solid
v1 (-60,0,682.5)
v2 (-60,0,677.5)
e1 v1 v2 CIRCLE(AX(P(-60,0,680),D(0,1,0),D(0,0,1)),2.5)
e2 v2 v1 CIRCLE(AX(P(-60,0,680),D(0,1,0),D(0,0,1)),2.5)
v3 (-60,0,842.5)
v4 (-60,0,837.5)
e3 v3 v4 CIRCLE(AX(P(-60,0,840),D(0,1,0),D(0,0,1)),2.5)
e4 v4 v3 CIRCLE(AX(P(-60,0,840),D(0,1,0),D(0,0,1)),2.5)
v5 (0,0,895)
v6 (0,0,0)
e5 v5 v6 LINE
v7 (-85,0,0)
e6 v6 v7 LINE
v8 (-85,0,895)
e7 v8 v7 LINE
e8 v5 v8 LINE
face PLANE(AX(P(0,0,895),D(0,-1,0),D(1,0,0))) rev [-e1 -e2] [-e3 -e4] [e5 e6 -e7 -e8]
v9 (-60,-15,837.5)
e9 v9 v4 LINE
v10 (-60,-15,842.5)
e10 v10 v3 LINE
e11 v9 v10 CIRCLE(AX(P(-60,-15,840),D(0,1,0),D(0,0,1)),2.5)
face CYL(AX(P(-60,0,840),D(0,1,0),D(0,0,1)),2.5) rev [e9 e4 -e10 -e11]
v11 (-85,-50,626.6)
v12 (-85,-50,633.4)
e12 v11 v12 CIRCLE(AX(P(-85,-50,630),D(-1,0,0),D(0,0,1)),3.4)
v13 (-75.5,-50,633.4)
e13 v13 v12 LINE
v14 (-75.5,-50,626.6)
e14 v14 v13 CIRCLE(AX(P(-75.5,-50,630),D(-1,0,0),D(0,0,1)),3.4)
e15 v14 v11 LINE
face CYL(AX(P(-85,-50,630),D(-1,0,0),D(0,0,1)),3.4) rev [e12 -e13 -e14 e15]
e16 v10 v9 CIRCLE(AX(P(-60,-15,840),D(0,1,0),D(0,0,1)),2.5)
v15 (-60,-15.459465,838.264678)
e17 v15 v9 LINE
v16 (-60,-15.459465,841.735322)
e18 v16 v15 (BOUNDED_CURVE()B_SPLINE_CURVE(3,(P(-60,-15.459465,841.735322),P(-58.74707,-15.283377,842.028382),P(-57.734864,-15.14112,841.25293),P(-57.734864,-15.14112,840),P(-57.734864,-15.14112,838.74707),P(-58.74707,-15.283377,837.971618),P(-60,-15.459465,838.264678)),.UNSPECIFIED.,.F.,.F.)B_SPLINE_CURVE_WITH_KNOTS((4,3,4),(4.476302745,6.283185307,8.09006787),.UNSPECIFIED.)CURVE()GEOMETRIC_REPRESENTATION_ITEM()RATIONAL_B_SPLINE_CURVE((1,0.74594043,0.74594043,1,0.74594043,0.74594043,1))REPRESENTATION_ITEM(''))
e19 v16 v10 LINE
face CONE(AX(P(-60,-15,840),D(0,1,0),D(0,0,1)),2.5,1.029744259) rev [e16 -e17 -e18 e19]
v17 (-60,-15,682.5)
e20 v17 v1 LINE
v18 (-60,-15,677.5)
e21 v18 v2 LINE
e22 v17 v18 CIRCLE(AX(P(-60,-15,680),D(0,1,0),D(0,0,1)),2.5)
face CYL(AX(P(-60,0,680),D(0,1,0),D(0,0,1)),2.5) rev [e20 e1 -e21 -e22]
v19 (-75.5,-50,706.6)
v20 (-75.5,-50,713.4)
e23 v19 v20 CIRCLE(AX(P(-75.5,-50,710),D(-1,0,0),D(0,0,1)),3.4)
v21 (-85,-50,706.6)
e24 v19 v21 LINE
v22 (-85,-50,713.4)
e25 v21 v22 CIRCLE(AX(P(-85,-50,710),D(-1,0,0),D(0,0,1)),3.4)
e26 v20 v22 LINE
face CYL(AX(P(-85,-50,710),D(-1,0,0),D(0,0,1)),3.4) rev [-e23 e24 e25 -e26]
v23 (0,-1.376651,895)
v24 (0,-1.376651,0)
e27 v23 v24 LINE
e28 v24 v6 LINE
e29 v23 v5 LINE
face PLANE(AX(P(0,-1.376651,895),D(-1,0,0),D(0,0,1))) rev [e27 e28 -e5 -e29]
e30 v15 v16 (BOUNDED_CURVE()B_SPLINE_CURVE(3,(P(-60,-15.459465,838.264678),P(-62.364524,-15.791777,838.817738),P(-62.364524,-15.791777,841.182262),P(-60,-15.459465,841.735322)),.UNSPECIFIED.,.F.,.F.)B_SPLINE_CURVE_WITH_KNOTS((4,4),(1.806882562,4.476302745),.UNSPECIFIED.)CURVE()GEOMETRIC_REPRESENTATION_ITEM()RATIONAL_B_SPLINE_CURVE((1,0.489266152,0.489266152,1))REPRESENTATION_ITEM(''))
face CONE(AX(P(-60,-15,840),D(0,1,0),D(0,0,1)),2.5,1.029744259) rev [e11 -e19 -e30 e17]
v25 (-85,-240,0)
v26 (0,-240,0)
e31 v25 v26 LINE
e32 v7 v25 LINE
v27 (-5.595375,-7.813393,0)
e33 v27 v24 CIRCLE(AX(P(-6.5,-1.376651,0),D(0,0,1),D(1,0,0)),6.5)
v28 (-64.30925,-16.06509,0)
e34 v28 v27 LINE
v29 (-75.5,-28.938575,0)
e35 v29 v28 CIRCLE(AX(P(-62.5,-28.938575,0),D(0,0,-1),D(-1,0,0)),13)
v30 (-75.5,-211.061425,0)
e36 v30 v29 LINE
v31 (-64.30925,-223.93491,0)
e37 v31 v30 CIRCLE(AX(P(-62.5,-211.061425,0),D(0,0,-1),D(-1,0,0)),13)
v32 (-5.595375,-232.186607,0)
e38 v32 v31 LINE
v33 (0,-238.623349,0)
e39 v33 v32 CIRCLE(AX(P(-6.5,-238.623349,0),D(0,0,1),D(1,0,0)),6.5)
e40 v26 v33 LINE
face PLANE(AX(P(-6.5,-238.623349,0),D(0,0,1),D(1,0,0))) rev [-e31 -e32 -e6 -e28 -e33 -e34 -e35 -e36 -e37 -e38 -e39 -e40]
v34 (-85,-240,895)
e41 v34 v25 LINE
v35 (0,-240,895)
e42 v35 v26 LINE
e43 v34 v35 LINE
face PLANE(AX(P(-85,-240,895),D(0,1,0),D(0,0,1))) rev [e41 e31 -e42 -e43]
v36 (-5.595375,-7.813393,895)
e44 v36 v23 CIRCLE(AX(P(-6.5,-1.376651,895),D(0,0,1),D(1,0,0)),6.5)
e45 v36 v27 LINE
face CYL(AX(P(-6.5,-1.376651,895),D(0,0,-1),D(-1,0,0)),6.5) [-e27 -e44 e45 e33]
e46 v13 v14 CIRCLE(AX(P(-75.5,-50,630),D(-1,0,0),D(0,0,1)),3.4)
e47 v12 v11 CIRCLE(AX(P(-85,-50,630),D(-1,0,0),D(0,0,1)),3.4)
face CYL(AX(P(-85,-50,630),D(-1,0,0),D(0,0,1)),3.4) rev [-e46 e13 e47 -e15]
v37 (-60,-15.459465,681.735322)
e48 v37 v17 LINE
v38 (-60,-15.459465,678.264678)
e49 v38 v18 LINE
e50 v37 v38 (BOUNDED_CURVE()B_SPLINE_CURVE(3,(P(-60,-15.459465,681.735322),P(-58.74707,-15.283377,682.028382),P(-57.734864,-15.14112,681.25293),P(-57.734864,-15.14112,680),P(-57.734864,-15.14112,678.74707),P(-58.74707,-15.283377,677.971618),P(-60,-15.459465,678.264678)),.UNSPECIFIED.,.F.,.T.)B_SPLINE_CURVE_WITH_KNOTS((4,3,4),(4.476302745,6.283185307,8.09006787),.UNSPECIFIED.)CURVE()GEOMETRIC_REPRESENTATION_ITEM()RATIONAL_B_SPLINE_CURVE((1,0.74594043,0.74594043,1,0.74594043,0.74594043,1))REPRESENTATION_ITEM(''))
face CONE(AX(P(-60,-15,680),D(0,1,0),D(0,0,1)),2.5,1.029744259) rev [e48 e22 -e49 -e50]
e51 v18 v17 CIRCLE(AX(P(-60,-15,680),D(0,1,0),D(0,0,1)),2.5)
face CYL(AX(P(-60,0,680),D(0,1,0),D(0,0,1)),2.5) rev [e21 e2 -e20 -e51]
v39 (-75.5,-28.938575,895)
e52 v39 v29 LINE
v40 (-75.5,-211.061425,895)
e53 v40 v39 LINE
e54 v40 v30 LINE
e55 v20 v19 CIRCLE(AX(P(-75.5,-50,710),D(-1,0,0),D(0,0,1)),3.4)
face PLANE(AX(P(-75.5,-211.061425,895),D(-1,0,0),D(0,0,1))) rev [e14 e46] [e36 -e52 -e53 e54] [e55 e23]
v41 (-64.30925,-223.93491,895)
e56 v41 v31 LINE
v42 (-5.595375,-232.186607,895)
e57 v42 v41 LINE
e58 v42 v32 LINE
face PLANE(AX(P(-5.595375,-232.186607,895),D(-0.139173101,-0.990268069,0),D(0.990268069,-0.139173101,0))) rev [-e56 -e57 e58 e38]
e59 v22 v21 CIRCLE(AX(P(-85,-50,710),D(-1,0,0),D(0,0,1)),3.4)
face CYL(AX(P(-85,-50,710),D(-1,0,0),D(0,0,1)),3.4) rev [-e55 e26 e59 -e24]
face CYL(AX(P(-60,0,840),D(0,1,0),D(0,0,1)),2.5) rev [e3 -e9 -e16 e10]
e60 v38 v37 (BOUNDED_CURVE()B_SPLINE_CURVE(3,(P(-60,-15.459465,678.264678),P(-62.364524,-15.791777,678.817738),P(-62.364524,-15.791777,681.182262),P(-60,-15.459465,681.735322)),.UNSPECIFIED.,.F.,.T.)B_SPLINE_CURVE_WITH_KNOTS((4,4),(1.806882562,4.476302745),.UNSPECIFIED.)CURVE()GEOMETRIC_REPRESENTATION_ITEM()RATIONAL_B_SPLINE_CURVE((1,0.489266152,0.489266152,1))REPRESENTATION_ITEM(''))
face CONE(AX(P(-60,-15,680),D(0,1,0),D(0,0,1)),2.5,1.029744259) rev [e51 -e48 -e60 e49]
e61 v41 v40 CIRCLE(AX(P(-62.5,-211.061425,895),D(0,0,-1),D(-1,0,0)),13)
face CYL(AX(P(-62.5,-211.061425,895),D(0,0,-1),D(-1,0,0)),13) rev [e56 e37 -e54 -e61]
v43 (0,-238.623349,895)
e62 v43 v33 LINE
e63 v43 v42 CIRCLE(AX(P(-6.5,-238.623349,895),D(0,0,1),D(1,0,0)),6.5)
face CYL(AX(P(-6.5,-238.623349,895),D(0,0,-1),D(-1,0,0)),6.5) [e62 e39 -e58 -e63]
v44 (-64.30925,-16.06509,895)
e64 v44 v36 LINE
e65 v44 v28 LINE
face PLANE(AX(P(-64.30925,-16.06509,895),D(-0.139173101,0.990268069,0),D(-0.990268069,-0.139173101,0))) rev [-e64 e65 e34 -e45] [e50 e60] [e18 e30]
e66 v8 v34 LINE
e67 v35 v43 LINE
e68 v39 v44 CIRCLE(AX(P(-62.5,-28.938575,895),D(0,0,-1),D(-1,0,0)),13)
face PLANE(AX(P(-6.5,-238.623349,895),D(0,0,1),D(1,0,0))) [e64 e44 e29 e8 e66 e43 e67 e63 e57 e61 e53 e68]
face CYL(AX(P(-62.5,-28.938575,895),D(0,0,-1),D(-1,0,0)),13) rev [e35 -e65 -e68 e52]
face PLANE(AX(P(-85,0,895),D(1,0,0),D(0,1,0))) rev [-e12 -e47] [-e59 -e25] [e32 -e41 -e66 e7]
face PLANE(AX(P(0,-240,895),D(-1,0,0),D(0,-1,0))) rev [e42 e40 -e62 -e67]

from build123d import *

# Parameters (mm, degrees)
EXTRUDE_1_DEPTH        = 895
HOLE_WIZARD_M8_1_D     = 6.8
HOLE_WIZARD_M8_1_DEPTH = 19.75
HOLE_WIZARD_M8_1_TIP   = 2.042926105
HOLE_WIZARD_M6_1_D     = 5
HOLE_WIZARD_M6_1_DEPTH = 15
HOLE_WIZARD_M6_1_TIP   = 1.502151548


with BuildPart() as part:
    # 草图1 → 凸台-拉伸1 (new body)
    with BuildSketch(Plane.XY):
        with BuildLine():
            Line((0, 0), (-85, 0))
            Line((-85, 0), (-85, -240))
            Line((-85, -240), (0, -240))
            Line((0, -240), (0, -238.623349271))
            ThreePointArc((0, -238.623349271), (-1.594387729, -234.358965582), (-5.595374844, -232.186606824))
            Line((-5.595374844, -232.186606824), (-64.309250312, -223.934909757))
            ThreePointArc((-64.309250312, -223.934909757), (-72.311224543, -219.59019224), (-75.5, -211.061424863))
            Line((-75.5, -211.061424863), (-75.5, -28.938575137))
            ThreePointArc((-75.5, -28.938575137), (-72.311224543, -20.40980776), (-64.309250312, -16.065090243))
            Line((-64.309250312, -16.065090243), (-5.595374844, -7.813393176))
            ThreePointArc((-5.595374844, -7.813393176), (-1.594387729, -5.641034418), (0, -1.376650729))
            Line((0, -1.376650729), (0, 0))
        make_face()
    extrude(amount=EXTRUDE_1_DEPTH)

    # M8 螺纹孔1
    with Locations(Plane.ZY.offset(85)):
        with Locations((630, -50), (710, -50)):
            Hole(HOLE_WIZARD_M8_1_D / 2, depth=HOLE_WIZARD_M8_1_DEPTH)
            with Locations((0, 0, -(HOLE_WIZARD_M8_1_DEPTH + HOLE_WIZARD_M8_1_TIP / 2))):  # 118° drill point
                Cone(0, HOLE_WIZARD_M8_1_D / 2, HOLE_WIZARD_M8_1_TIP, mode=Mode.SUBTRACT)

    # M6 螺纹孔1
    with Locations(Plane(origin=(0, 0, 0), x_dir=(1, 0, 0), z_dir=(0, 1, 0))):
        with Locations((-60, -840), (-60, -680)):
            Hole(HOLE_WIZARD_M6_1_D / 2, depth=HOLE_WIZARD_M6_1_DEPTH)
            with Locations((0, 0, -(HOLE_WIZARD_M6_1_DEPTH + HOLE_WIZARD_M6_1_TIP / 2))):  # 118° drill point
                Cone(0, HOLE_WIZARD_M6_1_D / 2, HOLE_WIZARD_M6_1_TIP, mode=Mode.SUBTRACT)


solid = part.part
